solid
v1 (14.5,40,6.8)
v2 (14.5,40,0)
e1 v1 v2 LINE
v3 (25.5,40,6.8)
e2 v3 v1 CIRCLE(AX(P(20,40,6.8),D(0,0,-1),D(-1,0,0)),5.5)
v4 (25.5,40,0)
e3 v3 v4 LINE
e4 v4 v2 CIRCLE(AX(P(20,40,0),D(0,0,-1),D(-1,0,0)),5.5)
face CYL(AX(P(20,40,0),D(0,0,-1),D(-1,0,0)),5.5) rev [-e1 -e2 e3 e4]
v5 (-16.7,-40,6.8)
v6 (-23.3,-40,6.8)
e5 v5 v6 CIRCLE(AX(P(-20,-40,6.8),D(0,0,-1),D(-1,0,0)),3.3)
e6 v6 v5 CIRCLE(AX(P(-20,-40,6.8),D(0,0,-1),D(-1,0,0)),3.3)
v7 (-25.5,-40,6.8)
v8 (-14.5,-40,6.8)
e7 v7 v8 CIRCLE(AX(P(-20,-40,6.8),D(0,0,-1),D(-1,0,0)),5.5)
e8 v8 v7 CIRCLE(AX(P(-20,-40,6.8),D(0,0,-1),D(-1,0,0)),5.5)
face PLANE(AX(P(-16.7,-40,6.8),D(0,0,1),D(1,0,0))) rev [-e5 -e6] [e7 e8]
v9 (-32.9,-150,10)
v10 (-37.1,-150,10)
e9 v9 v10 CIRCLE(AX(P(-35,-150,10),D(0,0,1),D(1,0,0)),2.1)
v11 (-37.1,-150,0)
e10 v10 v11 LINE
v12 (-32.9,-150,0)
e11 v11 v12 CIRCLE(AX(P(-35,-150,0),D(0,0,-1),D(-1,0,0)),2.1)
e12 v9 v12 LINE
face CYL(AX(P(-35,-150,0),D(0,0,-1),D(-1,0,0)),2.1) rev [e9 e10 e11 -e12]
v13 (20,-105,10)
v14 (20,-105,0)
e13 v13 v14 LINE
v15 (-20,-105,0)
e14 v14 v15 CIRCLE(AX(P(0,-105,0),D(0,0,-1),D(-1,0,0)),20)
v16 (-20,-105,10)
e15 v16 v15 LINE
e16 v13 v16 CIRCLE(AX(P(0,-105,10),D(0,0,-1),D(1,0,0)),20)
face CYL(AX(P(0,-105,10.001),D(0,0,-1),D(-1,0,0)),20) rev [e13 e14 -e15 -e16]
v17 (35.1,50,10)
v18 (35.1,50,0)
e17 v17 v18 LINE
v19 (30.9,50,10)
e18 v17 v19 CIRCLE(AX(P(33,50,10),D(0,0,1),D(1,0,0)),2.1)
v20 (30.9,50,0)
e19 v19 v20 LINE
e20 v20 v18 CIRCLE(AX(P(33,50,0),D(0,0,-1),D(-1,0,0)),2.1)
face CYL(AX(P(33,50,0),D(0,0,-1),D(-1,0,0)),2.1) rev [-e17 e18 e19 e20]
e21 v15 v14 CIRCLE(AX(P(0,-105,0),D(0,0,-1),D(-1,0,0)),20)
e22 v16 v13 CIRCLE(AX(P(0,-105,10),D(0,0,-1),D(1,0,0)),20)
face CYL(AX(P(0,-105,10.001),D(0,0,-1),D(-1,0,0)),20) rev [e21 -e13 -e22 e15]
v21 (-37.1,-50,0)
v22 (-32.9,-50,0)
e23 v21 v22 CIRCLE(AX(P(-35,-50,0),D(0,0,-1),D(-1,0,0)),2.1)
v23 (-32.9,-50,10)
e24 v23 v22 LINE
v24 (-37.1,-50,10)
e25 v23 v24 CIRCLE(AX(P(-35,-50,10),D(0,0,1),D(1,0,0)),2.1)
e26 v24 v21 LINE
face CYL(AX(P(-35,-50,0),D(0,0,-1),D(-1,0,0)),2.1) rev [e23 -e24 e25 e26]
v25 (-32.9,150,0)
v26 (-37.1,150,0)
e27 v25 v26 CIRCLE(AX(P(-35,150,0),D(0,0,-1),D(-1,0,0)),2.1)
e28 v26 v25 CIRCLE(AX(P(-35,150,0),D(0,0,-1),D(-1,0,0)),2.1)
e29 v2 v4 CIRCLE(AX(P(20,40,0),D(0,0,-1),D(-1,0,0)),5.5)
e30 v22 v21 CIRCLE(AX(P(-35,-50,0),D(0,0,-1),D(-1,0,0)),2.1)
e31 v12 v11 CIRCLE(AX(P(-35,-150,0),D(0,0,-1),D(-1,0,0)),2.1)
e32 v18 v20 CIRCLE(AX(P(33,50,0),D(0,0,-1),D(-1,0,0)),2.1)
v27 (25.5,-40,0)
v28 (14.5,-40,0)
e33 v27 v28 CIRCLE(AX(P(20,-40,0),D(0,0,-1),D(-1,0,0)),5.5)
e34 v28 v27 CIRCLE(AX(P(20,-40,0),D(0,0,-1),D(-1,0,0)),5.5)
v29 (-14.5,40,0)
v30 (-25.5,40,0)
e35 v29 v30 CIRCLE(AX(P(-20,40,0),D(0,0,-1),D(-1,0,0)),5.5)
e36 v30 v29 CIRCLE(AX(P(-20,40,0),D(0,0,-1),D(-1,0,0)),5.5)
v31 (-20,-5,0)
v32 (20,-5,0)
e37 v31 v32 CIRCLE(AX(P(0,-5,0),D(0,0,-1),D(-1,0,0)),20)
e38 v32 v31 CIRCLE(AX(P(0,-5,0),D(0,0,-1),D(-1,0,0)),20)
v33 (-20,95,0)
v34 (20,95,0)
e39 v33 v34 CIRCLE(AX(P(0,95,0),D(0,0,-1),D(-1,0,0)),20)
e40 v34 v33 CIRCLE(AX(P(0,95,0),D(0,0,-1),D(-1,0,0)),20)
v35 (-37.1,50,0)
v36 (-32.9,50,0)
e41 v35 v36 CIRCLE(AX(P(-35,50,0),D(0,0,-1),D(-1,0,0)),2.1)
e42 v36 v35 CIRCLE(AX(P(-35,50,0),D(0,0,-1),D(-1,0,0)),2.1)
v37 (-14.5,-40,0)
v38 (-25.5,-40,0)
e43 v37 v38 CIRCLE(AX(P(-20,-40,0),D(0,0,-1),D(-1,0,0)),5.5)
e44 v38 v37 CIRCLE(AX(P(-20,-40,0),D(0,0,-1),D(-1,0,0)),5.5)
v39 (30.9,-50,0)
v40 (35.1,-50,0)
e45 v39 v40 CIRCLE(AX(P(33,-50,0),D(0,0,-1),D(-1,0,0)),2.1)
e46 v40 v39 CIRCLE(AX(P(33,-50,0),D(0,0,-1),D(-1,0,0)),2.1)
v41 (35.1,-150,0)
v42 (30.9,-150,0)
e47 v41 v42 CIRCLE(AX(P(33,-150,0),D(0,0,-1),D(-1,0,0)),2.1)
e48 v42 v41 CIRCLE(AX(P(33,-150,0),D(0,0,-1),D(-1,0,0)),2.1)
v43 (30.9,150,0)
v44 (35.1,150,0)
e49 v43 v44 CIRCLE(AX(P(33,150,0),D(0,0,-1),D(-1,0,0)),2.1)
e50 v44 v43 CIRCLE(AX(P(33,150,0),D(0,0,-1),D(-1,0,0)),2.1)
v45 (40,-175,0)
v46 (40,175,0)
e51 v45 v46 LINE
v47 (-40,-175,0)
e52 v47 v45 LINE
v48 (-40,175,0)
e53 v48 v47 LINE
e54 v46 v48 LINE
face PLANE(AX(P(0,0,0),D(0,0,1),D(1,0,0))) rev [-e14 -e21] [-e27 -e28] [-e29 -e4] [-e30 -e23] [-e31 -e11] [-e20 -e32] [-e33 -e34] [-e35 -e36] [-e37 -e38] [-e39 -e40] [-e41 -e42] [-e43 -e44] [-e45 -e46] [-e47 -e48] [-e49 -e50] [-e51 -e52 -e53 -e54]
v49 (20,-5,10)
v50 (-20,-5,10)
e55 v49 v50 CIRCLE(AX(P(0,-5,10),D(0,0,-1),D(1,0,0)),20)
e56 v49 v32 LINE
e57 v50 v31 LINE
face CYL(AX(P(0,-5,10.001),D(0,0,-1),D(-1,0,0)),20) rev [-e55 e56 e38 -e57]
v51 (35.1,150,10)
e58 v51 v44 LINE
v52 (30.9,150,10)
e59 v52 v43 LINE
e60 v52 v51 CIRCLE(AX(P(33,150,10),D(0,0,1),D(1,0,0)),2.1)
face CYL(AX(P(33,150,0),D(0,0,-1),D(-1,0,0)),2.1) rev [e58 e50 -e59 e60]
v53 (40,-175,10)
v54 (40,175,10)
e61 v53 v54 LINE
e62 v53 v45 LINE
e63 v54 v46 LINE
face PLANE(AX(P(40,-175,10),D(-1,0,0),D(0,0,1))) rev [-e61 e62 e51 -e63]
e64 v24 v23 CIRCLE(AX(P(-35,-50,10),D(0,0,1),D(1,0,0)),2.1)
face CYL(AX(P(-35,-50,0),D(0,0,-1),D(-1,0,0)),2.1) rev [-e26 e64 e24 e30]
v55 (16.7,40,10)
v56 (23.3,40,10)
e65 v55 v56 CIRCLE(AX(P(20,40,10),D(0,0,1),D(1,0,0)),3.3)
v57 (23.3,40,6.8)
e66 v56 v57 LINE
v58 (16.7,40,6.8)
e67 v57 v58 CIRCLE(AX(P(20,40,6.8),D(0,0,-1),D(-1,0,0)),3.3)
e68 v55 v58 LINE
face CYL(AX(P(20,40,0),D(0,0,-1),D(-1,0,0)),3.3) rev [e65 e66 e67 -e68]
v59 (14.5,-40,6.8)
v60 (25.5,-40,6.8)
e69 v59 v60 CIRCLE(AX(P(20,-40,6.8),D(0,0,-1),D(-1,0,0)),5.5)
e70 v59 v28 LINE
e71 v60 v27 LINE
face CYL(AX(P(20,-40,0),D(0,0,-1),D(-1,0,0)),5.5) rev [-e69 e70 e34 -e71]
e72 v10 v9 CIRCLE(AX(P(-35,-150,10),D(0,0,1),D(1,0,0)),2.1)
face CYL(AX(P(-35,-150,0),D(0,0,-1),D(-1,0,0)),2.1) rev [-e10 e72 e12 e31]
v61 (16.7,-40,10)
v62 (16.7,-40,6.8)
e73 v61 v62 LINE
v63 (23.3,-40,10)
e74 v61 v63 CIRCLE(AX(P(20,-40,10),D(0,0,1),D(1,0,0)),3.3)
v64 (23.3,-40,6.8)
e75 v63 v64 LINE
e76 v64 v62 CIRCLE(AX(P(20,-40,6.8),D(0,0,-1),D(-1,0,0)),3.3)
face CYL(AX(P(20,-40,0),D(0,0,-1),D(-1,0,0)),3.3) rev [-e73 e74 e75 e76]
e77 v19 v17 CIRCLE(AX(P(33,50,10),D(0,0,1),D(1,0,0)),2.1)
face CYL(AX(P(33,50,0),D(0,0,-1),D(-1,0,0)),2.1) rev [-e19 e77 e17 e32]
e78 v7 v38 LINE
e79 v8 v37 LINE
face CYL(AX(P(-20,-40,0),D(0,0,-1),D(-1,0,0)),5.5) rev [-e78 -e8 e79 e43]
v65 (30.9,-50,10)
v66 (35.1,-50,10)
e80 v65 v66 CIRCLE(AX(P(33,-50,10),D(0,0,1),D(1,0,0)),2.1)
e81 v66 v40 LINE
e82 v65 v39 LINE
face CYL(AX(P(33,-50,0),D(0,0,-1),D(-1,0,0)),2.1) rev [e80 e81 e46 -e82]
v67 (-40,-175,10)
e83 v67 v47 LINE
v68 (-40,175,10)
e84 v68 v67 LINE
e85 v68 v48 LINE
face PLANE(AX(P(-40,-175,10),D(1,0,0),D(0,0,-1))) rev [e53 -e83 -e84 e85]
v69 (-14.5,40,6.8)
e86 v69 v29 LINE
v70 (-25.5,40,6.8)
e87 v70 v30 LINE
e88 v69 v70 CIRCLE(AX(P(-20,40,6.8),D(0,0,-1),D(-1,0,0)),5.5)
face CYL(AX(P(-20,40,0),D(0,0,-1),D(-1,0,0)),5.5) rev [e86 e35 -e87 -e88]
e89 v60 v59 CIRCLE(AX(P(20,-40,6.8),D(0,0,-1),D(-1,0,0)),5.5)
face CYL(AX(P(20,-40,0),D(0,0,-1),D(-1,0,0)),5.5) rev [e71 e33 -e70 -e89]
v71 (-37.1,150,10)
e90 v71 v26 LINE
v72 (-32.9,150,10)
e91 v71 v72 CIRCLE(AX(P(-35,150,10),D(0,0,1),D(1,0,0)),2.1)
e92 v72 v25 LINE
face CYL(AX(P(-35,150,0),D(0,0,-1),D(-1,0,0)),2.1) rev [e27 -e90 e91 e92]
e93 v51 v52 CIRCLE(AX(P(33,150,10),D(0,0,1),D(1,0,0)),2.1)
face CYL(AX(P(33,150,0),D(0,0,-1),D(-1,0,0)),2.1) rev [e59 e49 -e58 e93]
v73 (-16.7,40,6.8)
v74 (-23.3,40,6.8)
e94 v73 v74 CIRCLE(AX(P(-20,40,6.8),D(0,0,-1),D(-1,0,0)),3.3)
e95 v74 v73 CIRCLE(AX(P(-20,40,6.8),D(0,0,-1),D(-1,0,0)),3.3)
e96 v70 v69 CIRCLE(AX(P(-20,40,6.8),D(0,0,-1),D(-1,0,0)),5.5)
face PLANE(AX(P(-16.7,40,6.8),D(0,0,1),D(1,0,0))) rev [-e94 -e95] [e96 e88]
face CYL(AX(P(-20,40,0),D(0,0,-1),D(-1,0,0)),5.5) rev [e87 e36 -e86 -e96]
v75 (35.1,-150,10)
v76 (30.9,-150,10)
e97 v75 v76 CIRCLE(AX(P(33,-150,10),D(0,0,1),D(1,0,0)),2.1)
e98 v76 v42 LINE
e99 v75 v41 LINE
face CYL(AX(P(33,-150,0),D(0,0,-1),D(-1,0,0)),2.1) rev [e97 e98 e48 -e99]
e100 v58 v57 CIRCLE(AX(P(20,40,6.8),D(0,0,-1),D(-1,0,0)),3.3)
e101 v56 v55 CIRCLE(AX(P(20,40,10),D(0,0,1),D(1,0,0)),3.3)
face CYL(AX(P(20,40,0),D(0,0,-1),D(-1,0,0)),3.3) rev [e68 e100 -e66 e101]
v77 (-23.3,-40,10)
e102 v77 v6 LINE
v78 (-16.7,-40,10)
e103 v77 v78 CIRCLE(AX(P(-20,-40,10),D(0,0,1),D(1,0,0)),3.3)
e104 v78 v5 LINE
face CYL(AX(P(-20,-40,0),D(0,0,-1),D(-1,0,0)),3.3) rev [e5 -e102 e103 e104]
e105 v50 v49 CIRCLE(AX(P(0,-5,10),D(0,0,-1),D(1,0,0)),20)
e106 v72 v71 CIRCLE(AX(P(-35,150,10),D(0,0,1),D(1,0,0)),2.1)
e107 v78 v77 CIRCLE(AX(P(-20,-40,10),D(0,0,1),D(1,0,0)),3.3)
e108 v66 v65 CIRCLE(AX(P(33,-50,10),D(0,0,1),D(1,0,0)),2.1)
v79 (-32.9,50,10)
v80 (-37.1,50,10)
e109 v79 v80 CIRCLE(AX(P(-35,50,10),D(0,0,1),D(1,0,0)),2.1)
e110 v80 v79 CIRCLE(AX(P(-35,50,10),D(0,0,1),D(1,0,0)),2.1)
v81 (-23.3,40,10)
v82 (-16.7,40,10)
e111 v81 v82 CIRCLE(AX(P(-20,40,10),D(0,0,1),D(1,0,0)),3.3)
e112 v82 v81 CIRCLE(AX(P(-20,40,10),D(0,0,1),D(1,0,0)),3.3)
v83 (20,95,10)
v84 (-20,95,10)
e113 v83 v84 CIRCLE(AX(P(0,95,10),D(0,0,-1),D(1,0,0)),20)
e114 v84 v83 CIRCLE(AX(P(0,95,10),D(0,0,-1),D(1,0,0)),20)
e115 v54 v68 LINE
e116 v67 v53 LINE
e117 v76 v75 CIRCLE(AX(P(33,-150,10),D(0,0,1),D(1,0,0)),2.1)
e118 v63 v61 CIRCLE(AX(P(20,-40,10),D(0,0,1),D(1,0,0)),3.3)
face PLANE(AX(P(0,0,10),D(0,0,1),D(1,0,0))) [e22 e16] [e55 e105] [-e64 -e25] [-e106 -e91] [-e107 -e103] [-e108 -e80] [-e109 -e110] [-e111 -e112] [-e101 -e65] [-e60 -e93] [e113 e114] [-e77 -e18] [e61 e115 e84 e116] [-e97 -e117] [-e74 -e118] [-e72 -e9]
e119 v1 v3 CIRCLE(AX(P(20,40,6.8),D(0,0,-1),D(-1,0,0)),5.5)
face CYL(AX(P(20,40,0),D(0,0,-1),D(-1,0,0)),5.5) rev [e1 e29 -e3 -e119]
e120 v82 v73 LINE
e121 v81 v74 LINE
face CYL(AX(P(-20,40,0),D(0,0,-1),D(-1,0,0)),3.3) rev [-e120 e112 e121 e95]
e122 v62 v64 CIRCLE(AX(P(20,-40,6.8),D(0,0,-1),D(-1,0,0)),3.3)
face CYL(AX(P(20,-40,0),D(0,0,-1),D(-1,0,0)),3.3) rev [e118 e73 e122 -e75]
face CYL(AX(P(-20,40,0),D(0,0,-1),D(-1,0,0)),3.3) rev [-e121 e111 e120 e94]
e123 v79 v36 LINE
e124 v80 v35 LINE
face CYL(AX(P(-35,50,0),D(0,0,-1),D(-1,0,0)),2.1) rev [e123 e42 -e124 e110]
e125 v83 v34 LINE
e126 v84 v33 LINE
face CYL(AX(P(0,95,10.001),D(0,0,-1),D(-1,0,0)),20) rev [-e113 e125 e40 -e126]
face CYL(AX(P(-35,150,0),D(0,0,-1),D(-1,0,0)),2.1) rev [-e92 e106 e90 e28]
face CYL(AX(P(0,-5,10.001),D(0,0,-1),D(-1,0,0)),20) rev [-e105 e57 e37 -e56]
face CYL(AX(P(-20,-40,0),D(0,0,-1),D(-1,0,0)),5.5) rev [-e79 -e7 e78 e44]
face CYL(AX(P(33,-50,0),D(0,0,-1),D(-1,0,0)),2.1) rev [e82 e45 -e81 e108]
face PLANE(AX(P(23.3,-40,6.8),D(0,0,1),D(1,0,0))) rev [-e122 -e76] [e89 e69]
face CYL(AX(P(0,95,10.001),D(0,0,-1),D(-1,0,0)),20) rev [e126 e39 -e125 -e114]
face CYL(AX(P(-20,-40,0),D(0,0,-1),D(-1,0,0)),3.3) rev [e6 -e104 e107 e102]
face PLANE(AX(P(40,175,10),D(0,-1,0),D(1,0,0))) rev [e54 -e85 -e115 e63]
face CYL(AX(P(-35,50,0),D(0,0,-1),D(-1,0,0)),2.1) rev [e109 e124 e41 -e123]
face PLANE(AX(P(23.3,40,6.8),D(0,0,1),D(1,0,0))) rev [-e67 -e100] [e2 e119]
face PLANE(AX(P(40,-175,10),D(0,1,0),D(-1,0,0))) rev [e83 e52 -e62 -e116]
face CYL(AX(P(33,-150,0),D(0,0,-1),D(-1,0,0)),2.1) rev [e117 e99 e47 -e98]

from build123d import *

# Parameters (mm, degrees)
SKETCH_1_W                = 80
SKETCH_1_H                = 350
EXTRUDE_1_DEPTH           = 10
HOLE_WIZARD_M5_1_D        = 4.2
HOLE_WIZARD_1_D           = 6.6
HOLE_WIZARD_1_CBORE_D     = 11
HOLE_WIZARD_1_CBORE_DEPTH = 6.8
CUT_EXTRUDE_1_REACH       = 181.792
SKETCH_6_R                = 20
PATTERN_LINEAR_1_COUNT    = 3
PATTERN_LINEAR_1_PITCH    = 100


with BuildPart() as part:
    # 草图1 → 凸台-拉伸1 (new body)
    with BuildSketch(Plane.XY):
        Rectangle(SKETCH_1_W, SKETCH_1_H)
    extrude(amount=EXTRUDE_1_DEPTH)

    # M5 螺纹孔1 (through all)
    with Locations(Plane(origin=(0, 0, 0), x_dir=(-1, 0, 0), z_dir=(0, 0, -1))):
        with Locations((-33.000000411, 150), (34.999999589, 150), (-33.000000411, 50), (34.999999589, 50), (-33.000000411, -50), (34.999999589, -50), (-33.000000411, -150), (34.999999589, -150)):
            Hole(HOLE_WIZARD_M5_1_D / 2)

    # 打孔尺寸(%根据)内六角圆柱头螺钉的类型1 (through all)
    with Locations(Plane(origin=(0, 0, 0), x_dir=(-1, 0, 0), z_dir=(0, 0, -1))):
        with Locations((-20, 40), (20, 40), (20, -40), (-20, -40)):
            CounterBoreHole(HOLE_WIZARD_1_D / 2, HOLE_WIZARD_1_CBORE_D / 2, HOLE_WIZARD_1_CBORE_DEPTH)

    # 草图6 → 切除-拉伸1 (cut, up to next)
    with BuildSketch(Plane(origin=(0, 0, 0), x_dir=(-1, 0, 0), z_dir=(0, 0, -1)), mode=Mode.PRIVATE) as cut_extrude_1_sk1:
        with Locations((0, -105)):
            Circle(SKETCH_6_R)
    cut_extrude_1_tool1 = extrude(cut_extrude_1_sk1.sketch, amount=-CUT_EXTRUDE_1_REACH, mode=Mode.PRIVATE) & part.part
    cut_extrude_1 = cut_extrude_1_tool1.solids().sort_by_distance((0, -105, 0))[0]
    add(cut_extrude_1, mode=Mode.SUBTRACT)

    # 阵列(线性)1: 切除-拉伸1 ×3
    with Locations(*[(0, i * PATTERN_LINEAR_1_PITCH, 0) for i in range(1, PATTERN_LINEAR_1_COUNT)]):
        add(cut_extrude_1, mode=Mode.SUBTRACT)


solid = part.part
